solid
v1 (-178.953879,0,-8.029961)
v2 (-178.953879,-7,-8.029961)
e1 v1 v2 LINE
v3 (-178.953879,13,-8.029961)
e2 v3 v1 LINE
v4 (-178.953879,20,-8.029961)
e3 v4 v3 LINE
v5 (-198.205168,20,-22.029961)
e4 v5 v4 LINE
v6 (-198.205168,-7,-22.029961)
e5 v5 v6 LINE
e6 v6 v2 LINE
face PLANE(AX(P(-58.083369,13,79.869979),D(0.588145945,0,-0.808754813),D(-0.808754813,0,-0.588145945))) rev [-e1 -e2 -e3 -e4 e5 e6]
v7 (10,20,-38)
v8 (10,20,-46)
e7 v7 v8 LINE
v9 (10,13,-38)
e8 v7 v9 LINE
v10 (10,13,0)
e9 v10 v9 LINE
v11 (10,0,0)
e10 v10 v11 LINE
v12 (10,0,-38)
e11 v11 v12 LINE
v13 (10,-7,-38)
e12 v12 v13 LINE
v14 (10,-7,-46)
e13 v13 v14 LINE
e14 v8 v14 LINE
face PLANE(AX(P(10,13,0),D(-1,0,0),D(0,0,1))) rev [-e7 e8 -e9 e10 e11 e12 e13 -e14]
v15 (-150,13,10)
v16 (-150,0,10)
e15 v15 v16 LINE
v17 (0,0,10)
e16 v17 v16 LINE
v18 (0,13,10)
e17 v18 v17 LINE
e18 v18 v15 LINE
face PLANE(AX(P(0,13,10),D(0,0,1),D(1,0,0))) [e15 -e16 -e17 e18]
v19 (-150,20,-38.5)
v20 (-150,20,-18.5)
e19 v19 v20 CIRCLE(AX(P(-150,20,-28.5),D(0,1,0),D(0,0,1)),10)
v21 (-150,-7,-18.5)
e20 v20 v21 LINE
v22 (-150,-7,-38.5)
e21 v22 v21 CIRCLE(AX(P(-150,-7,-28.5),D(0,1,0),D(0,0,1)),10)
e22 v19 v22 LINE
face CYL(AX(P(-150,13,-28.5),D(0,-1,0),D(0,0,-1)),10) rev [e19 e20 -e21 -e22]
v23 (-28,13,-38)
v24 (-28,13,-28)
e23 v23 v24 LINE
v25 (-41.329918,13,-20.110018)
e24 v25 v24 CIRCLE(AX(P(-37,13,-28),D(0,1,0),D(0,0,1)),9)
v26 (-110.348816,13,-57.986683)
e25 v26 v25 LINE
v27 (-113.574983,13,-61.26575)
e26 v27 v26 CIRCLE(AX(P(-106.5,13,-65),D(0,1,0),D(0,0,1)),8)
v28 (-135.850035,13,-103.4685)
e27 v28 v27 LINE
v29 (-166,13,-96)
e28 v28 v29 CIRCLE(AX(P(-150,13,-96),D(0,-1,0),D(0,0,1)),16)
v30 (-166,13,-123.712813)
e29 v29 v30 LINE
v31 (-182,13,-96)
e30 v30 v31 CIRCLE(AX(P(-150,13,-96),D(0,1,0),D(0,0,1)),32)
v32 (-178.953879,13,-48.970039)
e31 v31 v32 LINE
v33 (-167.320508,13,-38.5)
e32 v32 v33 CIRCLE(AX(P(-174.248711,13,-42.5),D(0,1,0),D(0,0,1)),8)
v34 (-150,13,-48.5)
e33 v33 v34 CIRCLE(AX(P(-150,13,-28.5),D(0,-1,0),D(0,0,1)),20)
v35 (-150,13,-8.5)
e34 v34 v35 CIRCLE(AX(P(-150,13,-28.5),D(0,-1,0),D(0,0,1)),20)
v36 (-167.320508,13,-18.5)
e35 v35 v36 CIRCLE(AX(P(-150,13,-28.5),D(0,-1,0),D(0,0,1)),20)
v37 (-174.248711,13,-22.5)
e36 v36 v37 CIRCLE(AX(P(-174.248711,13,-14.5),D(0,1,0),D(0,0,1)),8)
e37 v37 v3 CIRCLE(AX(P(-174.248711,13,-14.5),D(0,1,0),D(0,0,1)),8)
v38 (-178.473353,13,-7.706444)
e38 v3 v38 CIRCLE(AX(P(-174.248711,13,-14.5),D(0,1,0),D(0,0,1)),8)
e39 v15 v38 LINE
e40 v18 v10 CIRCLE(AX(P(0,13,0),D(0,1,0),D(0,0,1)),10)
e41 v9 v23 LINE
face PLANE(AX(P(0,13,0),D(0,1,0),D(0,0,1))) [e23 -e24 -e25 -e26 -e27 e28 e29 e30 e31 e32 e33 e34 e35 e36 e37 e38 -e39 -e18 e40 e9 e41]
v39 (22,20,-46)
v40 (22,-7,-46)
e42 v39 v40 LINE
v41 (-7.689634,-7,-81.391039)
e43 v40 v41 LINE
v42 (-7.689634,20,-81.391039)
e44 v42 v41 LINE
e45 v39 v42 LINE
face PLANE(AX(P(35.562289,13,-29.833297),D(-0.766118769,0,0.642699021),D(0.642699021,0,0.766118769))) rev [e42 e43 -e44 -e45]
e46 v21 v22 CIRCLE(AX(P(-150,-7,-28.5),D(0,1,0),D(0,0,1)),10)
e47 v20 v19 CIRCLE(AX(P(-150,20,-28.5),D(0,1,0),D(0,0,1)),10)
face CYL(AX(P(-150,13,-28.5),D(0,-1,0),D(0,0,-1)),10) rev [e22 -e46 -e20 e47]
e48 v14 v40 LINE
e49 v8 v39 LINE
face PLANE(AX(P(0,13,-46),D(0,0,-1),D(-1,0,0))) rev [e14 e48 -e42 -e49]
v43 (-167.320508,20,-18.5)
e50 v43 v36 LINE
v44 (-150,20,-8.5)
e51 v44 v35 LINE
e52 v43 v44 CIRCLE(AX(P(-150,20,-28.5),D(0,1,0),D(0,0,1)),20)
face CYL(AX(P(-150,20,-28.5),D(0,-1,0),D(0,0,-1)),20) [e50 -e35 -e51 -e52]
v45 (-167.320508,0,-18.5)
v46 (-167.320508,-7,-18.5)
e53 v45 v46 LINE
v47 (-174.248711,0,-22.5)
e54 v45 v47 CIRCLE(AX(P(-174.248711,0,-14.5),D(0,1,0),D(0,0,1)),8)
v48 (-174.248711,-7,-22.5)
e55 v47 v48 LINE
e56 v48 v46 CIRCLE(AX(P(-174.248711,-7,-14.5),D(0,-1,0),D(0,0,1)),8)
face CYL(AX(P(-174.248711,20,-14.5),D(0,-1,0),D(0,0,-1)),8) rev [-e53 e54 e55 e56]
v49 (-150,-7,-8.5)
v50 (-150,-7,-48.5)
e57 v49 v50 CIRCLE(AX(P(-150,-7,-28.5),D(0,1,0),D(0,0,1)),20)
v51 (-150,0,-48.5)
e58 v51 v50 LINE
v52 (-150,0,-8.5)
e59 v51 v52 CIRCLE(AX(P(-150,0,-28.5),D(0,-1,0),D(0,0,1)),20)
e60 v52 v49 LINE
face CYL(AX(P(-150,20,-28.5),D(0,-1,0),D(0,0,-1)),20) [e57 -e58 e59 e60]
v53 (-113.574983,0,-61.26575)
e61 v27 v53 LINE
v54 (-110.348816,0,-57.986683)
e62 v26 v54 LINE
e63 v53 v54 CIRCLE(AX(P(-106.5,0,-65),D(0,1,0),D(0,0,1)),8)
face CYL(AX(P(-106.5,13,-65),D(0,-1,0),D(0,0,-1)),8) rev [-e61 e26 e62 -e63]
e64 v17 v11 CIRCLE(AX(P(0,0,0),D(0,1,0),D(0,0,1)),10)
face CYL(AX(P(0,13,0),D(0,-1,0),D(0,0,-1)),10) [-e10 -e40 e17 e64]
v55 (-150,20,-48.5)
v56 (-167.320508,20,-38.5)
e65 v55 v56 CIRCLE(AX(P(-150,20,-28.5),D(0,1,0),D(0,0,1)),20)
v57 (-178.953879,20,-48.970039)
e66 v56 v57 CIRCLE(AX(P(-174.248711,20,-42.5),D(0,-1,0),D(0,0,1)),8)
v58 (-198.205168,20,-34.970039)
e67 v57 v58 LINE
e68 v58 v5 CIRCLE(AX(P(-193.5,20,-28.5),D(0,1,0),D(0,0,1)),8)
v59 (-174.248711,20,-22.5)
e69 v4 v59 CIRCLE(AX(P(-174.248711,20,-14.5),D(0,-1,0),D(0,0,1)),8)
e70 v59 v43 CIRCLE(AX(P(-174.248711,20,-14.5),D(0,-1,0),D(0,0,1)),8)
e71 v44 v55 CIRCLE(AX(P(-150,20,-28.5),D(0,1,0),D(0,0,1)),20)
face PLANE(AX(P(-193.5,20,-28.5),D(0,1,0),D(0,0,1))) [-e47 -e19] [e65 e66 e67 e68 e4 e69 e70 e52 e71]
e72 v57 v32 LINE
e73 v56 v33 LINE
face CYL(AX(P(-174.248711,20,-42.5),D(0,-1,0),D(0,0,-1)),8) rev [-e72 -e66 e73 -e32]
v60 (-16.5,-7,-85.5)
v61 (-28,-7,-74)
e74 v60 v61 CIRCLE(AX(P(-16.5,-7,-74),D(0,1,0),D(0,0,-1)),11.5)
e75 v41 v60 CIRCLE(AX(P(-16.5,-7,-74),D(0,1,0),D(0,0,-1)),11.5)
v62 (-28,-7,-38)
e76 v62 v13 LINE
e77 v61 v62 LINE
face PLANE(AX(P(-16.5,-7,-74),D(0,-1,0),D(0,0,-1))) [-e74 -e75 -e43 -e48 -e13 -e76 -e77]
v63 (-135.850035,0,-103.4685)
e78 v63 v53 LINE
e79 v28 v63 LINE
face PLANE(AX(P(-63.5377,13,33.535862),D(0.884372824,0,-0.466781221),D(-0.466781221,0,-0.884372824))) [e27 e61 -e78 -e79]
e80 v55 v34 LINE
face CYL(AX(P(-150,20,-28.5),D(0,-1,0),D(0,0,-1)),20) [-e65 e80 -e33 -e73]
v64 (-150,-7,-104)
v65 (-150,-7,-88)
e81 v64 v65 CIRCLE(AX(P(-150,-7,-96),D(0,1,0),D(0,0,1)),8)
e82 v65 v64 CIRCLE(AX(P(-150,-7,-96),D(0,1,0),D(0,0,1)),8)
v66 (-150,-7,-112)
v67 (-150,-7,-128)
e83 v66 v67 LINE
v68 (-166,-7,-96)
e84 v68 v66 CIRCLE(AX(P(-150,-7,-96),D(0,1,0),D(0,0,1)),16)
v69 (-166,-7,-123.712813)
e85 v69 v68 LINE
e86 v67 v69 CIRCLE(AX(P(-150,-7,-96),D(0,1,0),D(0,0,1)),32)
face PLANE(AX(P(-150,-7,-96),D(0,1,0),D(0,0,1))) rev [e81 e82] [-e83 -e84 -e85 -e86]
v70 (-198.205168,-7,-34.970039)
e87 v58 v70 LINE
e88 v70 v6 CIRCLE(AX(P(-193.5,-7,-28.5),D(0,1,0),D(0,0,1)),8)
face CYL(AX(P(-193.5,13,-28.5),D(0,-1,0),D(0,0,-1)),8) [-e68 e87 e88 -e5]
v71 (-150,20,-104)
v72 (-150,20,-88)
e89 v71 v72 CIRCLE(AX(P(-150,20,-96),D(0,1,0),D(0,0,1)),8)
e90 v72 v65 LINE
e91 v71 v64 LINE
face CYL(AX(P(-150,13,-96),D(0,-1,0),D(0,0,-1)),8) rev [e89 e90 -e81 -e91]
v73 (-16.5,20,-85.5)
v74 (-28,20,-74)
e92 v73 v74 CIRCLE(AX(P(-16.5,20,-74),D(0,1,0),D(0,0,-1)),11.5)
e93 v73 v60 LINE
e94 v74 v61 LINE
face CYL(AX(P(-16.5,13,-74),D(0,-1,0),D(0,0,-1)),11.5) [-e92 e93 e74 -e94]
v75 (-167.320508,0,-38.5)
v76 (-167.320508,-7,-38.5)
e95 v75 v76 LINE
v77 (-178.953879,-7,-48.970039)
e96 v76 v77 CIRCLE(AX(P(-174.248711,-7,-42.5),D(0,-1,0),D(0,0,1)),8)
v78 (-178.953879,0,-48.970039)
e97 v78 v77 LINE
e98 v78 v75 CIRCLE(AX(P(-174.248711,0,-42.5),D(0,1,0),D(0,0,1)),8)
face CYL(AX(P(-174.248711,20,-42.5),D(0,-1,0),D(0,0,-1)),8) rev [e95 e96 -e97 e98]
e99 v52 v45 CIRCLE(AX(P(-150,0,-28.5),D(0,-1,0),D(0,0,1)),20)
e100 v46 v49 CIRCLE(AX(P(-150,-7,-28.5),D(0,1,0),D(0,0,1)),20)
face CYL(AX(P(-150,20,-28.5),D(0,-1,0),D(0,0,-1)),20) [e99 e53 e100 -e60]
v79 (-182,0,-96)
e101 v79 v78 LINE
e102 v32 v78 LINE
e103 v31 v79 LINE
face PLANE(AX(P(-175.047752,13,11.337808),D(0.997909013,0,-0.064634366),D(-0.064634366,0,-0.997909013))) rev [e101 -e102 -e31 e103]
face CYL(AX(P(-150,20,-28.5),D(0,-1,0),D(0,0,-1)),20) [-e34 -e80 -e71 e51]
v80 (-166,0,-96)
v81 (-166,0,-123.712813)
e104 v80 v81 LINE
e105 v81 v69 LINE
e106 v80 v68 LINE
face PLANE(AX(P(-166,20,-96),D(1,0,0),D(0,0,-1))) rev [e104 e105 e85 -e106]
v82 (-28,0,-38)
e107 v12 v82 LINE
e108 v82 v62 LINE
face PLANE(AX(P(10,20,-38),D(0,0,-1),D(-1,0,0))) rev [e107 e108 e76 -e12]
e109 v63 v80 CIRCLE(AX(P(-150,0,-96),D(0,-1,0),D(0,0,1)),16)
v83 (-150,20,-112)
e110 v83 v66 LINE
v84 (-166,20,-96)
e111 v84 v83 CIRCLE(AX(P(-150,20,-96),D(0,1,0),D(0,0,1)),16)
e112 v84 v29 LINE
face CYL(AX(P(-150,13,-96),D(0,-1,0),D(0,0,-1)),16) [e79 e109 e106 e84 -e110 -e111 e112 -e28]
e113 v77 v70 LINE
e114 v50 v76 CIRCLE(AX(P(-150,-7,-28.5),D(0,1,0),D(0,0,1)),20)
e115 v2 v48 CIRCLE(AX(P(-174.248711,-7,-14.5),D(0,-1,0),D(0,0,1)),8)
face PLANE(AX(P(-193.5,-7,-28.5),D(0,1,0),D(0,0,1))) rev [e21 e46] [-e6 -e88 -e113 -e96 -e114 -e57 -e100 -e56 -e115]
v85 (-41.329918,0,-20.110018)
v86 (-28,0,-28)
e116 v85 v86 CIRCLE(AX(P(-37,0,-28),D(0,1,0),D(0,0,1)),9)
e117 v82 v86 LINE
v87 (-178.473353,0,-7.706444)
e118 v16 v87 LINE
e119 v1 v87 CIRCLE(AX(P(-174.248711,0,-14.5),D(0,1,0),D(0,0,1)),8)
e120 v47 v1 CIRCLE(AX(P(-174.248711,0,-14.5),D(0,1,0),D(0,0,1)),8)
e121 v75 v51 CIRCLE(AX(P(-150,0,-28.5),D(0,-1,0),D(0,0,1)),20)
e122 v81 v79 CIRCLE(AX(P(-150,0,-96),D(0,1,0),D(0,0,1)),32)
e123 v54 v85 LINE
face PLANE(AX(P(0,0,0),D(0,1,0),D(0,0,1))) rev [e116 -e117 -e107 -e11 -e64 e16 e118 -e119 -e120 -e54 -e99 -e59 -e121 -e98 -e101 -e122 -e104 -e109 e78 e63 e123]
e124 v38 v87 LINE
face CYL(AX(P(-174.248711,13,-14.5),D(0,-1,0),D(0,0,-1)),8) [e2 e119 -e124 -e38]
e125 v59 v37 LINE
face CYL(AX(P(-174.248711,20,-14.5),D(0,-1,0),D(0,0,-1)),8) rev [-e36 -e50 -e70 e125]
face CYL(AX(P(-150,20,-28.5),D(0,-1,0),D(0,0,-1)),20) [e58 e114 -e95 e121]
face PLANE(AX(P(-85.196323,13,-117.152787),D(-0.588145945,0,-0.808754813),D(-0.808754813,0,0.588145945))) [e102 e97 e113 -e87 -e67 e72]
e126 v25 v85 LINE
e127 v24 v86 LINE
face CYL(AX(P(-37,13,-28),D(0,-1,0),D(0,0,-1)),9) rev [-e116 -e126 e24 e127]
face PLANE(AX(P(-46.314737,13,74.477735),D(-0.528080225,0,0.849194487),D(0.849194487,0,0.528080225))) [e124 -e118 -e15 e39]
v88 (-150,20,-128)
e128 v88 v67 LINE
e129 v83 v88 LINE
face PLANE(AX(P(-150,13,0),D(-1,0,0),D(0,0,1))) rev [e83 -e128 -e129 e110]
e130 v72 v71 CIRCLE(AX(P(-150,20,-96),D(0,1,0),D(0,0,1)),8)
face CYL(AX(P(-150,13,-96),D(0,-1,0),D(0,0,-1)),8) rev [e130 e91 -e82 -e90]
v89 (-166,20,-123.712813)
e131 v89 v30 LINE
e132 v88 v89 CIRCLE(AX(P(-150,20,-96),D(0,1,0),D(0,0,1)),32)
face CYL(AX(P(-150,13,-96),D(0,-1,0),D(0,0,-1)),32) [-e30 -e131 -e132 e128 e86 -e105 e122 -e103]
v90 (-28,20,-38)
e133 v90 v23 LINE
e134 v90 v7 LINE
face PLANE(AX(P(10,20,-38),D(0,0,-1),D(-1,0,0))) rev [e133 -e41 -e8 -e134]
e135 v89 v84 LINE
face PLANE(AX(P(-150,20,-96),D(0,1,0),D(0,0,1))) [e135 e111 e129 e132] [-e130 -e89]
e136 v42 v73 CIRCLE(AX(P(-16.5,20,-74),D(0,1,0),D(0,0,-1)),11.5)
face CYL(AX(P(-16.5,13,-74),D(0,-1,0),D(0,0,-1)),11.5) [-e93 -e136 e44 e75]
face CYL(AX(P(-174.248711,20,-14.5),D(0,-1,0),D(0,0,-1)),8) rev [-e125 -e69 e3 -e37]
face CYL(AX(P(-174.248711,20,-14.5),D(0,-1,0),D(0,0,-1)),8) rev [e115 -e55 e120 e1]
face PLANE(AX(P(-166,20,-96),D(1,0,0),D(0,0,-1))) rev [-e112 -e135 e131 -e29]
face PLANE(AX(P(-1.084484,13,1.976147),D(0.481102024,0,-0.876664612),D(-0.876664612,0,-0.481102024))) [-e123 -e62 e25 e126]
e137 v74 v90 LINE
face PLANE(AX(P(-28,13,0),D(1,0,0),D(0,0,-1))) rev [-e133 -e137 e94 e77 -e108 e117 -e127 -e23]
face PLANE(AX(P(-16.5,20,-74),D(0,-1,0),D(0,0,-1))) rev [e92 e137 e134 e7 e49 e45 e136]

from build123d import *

# Parameters (mm, degrees)
LEVER_PLATE_PROFILE_R   = 10
LEVER_PLATE_PROFILE_R_2 = 8
LEVER_PLATE_DEPTH       = 13
PIVOT_BOSS_PROFILE_R    = 8
PIVOT_BOSS_PROFILE_R_2  = 10
PIVOT_BOSSES_DEPTH      = 13.5


with BuildPart() as part:
    # Lever Plate Profile → Lever Plate (new body)
    with BuildSketch(Plane(origin=(0, 0, 0), x_dir=(1, 0, 0), z_dir=(0, 1, 0))):
        with BuildLine():
            Line((-150, -10), (0, -10))
            ThreePointArc((0, -10), (7.071067812, -7.071067812), (10, 0))
            Line((10, 0), (10, 46))
            Line((10, 46), (22, 46))
            Line((22, 46), (-7.689634159, 81.391038746))
            ThreePointArc((-7.689634159, 81.391038746), (-20.432606822, 84.806692537), (-28, 74))
            Line((-28, 74), (-28, 28))
            ThreePointArc((-28, 28), (-32.415747822, 20.255025373), (-41.329918215, 20.110018488))
            Line((-41.329918215, 20.110018488), (-110.348816191, 57.986683101))
            ThreePointArc((-110.348816191, 57.986683101), (-112.202667383, 59.389332952), (-113.574982592, 61.265750233))
            Line((-113.574982592, 61.265750233), (-135.850034815, 103.468499533))
            ThreePointArc((-135.850034815, 103.468499533), (-141.738522908, 109.702116489), (-150, 112))
            Line((-150, 112), (-150, 128))
            ThreePointArc((-150, 128), (-172.627416998, 118.627416998), (-182, 96))
            Line((-182, 96), (-178.953878866, 48.970038503))
            Line((-178.953878866, 48.970038503), (-198.20516756, 34.970038503))
            ThreePointArc((-198.20516756, 34.970038503), (-201.5, 28.5), (-198.20516756, 22.029961497))
            Line((-198.20516756, 22.029961497), (-178.953878866, 8.029961497))
            ThreePointArc((-178.953878866, 8.029961497), (-178.716545197, 7.863851996), (-178.473353106, 7.706444107))
            Line((-178.473353106, 7.706444107), (-150, -10))
        make_face()
        with Locations(Location((-150, 28.5, 0), (0, 0, 90))):
            Circle(LEVER_PLATE_PROFILE_R, mode=Mode.SUBTRACT)
        with Locations(Location((-150, 96, 0), (0, 0, 90))):
            Circle(LEVER_PLATE_PROFILE_R_2, mode=Mode.SUBTRACT)
    extrude(amount=LEVER_PLATE_DEPTH)

    # Pivot Boss Profile → Pivot Bosses (add, symmetric)
    # profile 1 of 3: a face of its own
    with BuildSketch(Plane(origin=(0, 6.5, 0), x_dir=(1, 0, 0), z_dir=(0, 1, 0))):
        with BuildLine():
            Line((-150, 112), (-150, 128))
            ThreePointArc((-150, 128), (-158.282209443, 126.909626441), (-166, 123.712812921))
            Line((-166, 123.712812921), (-166, 96))
            ThreePointArc((-166, 96), (-138.686291501, 84.686291501), (-150, 112))
        make_face()
        with Locations(Location((-150, 96, 0), (0, 0, 90))):
            Circle(PIVOT_BOSS_PROFILE_R, mode=Mode.SUBTRACT)
    # profile 2 of 3: a face of its own
    with BuildSketch(Plane(origin=(0, 6.5, 0), x_dir=(1, 0, 0), z_dir=(0, 1, 0))):
        with BuildLine():
            Line((-198.20516756, 34.970038503), (-178.953878866, 48.970038503))
            ThreePointArc((-178.953878866, 48.970038503), (-179.600430512, 36.553648048), (-167.320508076, 38.5))
            ThreePointArc((-167.320508076, 38.5), (-130, 28.5), (-167.320508076, 18.5))
            ThreePointArc((-167.320508076, 18.5), (-179.600430512, 20.446351952), (-178.953878866, 8.029961497))
            Line((-178.953878866, 8.029961497), (-198.20516756, 22.029961497))
            ThreePointArc((-198.20516756, 22.029961497), (-201.5, 28.5), (-198.20516756, 34.970038503))
        make_face()
        with Locations(Location((-150, 28.5, 0), (0, 0, 90))):
            Circle(PIVOT_BOSS_PROFILE_R_2, mode=Mode.SUBTRACT)
    # profile 3 of 3: a face of its own
    with BuildSketch(Plane(origin=(0, 6.5, 0), x_dir=(1, 0, 0), z_dir=(0, 1, 0))):
        with BuildLine():
            Line((-7.689634159, 81.391038746), (22, 46))
            Line((22, 46), (10, 46))
            Line((10, 46), (10, 38))
            Line((10, 38), (-28, 38))
            Line((-28, 38), (-28, 74))
            ThreePointArc((-28, 74), (-20.432606822, 84.806692537), (-7.689634159, 81.391038746))
        make_face()
    extrude(amount=PIVOT_BOSSES_DEPTH, both=True)


solid = part.part
